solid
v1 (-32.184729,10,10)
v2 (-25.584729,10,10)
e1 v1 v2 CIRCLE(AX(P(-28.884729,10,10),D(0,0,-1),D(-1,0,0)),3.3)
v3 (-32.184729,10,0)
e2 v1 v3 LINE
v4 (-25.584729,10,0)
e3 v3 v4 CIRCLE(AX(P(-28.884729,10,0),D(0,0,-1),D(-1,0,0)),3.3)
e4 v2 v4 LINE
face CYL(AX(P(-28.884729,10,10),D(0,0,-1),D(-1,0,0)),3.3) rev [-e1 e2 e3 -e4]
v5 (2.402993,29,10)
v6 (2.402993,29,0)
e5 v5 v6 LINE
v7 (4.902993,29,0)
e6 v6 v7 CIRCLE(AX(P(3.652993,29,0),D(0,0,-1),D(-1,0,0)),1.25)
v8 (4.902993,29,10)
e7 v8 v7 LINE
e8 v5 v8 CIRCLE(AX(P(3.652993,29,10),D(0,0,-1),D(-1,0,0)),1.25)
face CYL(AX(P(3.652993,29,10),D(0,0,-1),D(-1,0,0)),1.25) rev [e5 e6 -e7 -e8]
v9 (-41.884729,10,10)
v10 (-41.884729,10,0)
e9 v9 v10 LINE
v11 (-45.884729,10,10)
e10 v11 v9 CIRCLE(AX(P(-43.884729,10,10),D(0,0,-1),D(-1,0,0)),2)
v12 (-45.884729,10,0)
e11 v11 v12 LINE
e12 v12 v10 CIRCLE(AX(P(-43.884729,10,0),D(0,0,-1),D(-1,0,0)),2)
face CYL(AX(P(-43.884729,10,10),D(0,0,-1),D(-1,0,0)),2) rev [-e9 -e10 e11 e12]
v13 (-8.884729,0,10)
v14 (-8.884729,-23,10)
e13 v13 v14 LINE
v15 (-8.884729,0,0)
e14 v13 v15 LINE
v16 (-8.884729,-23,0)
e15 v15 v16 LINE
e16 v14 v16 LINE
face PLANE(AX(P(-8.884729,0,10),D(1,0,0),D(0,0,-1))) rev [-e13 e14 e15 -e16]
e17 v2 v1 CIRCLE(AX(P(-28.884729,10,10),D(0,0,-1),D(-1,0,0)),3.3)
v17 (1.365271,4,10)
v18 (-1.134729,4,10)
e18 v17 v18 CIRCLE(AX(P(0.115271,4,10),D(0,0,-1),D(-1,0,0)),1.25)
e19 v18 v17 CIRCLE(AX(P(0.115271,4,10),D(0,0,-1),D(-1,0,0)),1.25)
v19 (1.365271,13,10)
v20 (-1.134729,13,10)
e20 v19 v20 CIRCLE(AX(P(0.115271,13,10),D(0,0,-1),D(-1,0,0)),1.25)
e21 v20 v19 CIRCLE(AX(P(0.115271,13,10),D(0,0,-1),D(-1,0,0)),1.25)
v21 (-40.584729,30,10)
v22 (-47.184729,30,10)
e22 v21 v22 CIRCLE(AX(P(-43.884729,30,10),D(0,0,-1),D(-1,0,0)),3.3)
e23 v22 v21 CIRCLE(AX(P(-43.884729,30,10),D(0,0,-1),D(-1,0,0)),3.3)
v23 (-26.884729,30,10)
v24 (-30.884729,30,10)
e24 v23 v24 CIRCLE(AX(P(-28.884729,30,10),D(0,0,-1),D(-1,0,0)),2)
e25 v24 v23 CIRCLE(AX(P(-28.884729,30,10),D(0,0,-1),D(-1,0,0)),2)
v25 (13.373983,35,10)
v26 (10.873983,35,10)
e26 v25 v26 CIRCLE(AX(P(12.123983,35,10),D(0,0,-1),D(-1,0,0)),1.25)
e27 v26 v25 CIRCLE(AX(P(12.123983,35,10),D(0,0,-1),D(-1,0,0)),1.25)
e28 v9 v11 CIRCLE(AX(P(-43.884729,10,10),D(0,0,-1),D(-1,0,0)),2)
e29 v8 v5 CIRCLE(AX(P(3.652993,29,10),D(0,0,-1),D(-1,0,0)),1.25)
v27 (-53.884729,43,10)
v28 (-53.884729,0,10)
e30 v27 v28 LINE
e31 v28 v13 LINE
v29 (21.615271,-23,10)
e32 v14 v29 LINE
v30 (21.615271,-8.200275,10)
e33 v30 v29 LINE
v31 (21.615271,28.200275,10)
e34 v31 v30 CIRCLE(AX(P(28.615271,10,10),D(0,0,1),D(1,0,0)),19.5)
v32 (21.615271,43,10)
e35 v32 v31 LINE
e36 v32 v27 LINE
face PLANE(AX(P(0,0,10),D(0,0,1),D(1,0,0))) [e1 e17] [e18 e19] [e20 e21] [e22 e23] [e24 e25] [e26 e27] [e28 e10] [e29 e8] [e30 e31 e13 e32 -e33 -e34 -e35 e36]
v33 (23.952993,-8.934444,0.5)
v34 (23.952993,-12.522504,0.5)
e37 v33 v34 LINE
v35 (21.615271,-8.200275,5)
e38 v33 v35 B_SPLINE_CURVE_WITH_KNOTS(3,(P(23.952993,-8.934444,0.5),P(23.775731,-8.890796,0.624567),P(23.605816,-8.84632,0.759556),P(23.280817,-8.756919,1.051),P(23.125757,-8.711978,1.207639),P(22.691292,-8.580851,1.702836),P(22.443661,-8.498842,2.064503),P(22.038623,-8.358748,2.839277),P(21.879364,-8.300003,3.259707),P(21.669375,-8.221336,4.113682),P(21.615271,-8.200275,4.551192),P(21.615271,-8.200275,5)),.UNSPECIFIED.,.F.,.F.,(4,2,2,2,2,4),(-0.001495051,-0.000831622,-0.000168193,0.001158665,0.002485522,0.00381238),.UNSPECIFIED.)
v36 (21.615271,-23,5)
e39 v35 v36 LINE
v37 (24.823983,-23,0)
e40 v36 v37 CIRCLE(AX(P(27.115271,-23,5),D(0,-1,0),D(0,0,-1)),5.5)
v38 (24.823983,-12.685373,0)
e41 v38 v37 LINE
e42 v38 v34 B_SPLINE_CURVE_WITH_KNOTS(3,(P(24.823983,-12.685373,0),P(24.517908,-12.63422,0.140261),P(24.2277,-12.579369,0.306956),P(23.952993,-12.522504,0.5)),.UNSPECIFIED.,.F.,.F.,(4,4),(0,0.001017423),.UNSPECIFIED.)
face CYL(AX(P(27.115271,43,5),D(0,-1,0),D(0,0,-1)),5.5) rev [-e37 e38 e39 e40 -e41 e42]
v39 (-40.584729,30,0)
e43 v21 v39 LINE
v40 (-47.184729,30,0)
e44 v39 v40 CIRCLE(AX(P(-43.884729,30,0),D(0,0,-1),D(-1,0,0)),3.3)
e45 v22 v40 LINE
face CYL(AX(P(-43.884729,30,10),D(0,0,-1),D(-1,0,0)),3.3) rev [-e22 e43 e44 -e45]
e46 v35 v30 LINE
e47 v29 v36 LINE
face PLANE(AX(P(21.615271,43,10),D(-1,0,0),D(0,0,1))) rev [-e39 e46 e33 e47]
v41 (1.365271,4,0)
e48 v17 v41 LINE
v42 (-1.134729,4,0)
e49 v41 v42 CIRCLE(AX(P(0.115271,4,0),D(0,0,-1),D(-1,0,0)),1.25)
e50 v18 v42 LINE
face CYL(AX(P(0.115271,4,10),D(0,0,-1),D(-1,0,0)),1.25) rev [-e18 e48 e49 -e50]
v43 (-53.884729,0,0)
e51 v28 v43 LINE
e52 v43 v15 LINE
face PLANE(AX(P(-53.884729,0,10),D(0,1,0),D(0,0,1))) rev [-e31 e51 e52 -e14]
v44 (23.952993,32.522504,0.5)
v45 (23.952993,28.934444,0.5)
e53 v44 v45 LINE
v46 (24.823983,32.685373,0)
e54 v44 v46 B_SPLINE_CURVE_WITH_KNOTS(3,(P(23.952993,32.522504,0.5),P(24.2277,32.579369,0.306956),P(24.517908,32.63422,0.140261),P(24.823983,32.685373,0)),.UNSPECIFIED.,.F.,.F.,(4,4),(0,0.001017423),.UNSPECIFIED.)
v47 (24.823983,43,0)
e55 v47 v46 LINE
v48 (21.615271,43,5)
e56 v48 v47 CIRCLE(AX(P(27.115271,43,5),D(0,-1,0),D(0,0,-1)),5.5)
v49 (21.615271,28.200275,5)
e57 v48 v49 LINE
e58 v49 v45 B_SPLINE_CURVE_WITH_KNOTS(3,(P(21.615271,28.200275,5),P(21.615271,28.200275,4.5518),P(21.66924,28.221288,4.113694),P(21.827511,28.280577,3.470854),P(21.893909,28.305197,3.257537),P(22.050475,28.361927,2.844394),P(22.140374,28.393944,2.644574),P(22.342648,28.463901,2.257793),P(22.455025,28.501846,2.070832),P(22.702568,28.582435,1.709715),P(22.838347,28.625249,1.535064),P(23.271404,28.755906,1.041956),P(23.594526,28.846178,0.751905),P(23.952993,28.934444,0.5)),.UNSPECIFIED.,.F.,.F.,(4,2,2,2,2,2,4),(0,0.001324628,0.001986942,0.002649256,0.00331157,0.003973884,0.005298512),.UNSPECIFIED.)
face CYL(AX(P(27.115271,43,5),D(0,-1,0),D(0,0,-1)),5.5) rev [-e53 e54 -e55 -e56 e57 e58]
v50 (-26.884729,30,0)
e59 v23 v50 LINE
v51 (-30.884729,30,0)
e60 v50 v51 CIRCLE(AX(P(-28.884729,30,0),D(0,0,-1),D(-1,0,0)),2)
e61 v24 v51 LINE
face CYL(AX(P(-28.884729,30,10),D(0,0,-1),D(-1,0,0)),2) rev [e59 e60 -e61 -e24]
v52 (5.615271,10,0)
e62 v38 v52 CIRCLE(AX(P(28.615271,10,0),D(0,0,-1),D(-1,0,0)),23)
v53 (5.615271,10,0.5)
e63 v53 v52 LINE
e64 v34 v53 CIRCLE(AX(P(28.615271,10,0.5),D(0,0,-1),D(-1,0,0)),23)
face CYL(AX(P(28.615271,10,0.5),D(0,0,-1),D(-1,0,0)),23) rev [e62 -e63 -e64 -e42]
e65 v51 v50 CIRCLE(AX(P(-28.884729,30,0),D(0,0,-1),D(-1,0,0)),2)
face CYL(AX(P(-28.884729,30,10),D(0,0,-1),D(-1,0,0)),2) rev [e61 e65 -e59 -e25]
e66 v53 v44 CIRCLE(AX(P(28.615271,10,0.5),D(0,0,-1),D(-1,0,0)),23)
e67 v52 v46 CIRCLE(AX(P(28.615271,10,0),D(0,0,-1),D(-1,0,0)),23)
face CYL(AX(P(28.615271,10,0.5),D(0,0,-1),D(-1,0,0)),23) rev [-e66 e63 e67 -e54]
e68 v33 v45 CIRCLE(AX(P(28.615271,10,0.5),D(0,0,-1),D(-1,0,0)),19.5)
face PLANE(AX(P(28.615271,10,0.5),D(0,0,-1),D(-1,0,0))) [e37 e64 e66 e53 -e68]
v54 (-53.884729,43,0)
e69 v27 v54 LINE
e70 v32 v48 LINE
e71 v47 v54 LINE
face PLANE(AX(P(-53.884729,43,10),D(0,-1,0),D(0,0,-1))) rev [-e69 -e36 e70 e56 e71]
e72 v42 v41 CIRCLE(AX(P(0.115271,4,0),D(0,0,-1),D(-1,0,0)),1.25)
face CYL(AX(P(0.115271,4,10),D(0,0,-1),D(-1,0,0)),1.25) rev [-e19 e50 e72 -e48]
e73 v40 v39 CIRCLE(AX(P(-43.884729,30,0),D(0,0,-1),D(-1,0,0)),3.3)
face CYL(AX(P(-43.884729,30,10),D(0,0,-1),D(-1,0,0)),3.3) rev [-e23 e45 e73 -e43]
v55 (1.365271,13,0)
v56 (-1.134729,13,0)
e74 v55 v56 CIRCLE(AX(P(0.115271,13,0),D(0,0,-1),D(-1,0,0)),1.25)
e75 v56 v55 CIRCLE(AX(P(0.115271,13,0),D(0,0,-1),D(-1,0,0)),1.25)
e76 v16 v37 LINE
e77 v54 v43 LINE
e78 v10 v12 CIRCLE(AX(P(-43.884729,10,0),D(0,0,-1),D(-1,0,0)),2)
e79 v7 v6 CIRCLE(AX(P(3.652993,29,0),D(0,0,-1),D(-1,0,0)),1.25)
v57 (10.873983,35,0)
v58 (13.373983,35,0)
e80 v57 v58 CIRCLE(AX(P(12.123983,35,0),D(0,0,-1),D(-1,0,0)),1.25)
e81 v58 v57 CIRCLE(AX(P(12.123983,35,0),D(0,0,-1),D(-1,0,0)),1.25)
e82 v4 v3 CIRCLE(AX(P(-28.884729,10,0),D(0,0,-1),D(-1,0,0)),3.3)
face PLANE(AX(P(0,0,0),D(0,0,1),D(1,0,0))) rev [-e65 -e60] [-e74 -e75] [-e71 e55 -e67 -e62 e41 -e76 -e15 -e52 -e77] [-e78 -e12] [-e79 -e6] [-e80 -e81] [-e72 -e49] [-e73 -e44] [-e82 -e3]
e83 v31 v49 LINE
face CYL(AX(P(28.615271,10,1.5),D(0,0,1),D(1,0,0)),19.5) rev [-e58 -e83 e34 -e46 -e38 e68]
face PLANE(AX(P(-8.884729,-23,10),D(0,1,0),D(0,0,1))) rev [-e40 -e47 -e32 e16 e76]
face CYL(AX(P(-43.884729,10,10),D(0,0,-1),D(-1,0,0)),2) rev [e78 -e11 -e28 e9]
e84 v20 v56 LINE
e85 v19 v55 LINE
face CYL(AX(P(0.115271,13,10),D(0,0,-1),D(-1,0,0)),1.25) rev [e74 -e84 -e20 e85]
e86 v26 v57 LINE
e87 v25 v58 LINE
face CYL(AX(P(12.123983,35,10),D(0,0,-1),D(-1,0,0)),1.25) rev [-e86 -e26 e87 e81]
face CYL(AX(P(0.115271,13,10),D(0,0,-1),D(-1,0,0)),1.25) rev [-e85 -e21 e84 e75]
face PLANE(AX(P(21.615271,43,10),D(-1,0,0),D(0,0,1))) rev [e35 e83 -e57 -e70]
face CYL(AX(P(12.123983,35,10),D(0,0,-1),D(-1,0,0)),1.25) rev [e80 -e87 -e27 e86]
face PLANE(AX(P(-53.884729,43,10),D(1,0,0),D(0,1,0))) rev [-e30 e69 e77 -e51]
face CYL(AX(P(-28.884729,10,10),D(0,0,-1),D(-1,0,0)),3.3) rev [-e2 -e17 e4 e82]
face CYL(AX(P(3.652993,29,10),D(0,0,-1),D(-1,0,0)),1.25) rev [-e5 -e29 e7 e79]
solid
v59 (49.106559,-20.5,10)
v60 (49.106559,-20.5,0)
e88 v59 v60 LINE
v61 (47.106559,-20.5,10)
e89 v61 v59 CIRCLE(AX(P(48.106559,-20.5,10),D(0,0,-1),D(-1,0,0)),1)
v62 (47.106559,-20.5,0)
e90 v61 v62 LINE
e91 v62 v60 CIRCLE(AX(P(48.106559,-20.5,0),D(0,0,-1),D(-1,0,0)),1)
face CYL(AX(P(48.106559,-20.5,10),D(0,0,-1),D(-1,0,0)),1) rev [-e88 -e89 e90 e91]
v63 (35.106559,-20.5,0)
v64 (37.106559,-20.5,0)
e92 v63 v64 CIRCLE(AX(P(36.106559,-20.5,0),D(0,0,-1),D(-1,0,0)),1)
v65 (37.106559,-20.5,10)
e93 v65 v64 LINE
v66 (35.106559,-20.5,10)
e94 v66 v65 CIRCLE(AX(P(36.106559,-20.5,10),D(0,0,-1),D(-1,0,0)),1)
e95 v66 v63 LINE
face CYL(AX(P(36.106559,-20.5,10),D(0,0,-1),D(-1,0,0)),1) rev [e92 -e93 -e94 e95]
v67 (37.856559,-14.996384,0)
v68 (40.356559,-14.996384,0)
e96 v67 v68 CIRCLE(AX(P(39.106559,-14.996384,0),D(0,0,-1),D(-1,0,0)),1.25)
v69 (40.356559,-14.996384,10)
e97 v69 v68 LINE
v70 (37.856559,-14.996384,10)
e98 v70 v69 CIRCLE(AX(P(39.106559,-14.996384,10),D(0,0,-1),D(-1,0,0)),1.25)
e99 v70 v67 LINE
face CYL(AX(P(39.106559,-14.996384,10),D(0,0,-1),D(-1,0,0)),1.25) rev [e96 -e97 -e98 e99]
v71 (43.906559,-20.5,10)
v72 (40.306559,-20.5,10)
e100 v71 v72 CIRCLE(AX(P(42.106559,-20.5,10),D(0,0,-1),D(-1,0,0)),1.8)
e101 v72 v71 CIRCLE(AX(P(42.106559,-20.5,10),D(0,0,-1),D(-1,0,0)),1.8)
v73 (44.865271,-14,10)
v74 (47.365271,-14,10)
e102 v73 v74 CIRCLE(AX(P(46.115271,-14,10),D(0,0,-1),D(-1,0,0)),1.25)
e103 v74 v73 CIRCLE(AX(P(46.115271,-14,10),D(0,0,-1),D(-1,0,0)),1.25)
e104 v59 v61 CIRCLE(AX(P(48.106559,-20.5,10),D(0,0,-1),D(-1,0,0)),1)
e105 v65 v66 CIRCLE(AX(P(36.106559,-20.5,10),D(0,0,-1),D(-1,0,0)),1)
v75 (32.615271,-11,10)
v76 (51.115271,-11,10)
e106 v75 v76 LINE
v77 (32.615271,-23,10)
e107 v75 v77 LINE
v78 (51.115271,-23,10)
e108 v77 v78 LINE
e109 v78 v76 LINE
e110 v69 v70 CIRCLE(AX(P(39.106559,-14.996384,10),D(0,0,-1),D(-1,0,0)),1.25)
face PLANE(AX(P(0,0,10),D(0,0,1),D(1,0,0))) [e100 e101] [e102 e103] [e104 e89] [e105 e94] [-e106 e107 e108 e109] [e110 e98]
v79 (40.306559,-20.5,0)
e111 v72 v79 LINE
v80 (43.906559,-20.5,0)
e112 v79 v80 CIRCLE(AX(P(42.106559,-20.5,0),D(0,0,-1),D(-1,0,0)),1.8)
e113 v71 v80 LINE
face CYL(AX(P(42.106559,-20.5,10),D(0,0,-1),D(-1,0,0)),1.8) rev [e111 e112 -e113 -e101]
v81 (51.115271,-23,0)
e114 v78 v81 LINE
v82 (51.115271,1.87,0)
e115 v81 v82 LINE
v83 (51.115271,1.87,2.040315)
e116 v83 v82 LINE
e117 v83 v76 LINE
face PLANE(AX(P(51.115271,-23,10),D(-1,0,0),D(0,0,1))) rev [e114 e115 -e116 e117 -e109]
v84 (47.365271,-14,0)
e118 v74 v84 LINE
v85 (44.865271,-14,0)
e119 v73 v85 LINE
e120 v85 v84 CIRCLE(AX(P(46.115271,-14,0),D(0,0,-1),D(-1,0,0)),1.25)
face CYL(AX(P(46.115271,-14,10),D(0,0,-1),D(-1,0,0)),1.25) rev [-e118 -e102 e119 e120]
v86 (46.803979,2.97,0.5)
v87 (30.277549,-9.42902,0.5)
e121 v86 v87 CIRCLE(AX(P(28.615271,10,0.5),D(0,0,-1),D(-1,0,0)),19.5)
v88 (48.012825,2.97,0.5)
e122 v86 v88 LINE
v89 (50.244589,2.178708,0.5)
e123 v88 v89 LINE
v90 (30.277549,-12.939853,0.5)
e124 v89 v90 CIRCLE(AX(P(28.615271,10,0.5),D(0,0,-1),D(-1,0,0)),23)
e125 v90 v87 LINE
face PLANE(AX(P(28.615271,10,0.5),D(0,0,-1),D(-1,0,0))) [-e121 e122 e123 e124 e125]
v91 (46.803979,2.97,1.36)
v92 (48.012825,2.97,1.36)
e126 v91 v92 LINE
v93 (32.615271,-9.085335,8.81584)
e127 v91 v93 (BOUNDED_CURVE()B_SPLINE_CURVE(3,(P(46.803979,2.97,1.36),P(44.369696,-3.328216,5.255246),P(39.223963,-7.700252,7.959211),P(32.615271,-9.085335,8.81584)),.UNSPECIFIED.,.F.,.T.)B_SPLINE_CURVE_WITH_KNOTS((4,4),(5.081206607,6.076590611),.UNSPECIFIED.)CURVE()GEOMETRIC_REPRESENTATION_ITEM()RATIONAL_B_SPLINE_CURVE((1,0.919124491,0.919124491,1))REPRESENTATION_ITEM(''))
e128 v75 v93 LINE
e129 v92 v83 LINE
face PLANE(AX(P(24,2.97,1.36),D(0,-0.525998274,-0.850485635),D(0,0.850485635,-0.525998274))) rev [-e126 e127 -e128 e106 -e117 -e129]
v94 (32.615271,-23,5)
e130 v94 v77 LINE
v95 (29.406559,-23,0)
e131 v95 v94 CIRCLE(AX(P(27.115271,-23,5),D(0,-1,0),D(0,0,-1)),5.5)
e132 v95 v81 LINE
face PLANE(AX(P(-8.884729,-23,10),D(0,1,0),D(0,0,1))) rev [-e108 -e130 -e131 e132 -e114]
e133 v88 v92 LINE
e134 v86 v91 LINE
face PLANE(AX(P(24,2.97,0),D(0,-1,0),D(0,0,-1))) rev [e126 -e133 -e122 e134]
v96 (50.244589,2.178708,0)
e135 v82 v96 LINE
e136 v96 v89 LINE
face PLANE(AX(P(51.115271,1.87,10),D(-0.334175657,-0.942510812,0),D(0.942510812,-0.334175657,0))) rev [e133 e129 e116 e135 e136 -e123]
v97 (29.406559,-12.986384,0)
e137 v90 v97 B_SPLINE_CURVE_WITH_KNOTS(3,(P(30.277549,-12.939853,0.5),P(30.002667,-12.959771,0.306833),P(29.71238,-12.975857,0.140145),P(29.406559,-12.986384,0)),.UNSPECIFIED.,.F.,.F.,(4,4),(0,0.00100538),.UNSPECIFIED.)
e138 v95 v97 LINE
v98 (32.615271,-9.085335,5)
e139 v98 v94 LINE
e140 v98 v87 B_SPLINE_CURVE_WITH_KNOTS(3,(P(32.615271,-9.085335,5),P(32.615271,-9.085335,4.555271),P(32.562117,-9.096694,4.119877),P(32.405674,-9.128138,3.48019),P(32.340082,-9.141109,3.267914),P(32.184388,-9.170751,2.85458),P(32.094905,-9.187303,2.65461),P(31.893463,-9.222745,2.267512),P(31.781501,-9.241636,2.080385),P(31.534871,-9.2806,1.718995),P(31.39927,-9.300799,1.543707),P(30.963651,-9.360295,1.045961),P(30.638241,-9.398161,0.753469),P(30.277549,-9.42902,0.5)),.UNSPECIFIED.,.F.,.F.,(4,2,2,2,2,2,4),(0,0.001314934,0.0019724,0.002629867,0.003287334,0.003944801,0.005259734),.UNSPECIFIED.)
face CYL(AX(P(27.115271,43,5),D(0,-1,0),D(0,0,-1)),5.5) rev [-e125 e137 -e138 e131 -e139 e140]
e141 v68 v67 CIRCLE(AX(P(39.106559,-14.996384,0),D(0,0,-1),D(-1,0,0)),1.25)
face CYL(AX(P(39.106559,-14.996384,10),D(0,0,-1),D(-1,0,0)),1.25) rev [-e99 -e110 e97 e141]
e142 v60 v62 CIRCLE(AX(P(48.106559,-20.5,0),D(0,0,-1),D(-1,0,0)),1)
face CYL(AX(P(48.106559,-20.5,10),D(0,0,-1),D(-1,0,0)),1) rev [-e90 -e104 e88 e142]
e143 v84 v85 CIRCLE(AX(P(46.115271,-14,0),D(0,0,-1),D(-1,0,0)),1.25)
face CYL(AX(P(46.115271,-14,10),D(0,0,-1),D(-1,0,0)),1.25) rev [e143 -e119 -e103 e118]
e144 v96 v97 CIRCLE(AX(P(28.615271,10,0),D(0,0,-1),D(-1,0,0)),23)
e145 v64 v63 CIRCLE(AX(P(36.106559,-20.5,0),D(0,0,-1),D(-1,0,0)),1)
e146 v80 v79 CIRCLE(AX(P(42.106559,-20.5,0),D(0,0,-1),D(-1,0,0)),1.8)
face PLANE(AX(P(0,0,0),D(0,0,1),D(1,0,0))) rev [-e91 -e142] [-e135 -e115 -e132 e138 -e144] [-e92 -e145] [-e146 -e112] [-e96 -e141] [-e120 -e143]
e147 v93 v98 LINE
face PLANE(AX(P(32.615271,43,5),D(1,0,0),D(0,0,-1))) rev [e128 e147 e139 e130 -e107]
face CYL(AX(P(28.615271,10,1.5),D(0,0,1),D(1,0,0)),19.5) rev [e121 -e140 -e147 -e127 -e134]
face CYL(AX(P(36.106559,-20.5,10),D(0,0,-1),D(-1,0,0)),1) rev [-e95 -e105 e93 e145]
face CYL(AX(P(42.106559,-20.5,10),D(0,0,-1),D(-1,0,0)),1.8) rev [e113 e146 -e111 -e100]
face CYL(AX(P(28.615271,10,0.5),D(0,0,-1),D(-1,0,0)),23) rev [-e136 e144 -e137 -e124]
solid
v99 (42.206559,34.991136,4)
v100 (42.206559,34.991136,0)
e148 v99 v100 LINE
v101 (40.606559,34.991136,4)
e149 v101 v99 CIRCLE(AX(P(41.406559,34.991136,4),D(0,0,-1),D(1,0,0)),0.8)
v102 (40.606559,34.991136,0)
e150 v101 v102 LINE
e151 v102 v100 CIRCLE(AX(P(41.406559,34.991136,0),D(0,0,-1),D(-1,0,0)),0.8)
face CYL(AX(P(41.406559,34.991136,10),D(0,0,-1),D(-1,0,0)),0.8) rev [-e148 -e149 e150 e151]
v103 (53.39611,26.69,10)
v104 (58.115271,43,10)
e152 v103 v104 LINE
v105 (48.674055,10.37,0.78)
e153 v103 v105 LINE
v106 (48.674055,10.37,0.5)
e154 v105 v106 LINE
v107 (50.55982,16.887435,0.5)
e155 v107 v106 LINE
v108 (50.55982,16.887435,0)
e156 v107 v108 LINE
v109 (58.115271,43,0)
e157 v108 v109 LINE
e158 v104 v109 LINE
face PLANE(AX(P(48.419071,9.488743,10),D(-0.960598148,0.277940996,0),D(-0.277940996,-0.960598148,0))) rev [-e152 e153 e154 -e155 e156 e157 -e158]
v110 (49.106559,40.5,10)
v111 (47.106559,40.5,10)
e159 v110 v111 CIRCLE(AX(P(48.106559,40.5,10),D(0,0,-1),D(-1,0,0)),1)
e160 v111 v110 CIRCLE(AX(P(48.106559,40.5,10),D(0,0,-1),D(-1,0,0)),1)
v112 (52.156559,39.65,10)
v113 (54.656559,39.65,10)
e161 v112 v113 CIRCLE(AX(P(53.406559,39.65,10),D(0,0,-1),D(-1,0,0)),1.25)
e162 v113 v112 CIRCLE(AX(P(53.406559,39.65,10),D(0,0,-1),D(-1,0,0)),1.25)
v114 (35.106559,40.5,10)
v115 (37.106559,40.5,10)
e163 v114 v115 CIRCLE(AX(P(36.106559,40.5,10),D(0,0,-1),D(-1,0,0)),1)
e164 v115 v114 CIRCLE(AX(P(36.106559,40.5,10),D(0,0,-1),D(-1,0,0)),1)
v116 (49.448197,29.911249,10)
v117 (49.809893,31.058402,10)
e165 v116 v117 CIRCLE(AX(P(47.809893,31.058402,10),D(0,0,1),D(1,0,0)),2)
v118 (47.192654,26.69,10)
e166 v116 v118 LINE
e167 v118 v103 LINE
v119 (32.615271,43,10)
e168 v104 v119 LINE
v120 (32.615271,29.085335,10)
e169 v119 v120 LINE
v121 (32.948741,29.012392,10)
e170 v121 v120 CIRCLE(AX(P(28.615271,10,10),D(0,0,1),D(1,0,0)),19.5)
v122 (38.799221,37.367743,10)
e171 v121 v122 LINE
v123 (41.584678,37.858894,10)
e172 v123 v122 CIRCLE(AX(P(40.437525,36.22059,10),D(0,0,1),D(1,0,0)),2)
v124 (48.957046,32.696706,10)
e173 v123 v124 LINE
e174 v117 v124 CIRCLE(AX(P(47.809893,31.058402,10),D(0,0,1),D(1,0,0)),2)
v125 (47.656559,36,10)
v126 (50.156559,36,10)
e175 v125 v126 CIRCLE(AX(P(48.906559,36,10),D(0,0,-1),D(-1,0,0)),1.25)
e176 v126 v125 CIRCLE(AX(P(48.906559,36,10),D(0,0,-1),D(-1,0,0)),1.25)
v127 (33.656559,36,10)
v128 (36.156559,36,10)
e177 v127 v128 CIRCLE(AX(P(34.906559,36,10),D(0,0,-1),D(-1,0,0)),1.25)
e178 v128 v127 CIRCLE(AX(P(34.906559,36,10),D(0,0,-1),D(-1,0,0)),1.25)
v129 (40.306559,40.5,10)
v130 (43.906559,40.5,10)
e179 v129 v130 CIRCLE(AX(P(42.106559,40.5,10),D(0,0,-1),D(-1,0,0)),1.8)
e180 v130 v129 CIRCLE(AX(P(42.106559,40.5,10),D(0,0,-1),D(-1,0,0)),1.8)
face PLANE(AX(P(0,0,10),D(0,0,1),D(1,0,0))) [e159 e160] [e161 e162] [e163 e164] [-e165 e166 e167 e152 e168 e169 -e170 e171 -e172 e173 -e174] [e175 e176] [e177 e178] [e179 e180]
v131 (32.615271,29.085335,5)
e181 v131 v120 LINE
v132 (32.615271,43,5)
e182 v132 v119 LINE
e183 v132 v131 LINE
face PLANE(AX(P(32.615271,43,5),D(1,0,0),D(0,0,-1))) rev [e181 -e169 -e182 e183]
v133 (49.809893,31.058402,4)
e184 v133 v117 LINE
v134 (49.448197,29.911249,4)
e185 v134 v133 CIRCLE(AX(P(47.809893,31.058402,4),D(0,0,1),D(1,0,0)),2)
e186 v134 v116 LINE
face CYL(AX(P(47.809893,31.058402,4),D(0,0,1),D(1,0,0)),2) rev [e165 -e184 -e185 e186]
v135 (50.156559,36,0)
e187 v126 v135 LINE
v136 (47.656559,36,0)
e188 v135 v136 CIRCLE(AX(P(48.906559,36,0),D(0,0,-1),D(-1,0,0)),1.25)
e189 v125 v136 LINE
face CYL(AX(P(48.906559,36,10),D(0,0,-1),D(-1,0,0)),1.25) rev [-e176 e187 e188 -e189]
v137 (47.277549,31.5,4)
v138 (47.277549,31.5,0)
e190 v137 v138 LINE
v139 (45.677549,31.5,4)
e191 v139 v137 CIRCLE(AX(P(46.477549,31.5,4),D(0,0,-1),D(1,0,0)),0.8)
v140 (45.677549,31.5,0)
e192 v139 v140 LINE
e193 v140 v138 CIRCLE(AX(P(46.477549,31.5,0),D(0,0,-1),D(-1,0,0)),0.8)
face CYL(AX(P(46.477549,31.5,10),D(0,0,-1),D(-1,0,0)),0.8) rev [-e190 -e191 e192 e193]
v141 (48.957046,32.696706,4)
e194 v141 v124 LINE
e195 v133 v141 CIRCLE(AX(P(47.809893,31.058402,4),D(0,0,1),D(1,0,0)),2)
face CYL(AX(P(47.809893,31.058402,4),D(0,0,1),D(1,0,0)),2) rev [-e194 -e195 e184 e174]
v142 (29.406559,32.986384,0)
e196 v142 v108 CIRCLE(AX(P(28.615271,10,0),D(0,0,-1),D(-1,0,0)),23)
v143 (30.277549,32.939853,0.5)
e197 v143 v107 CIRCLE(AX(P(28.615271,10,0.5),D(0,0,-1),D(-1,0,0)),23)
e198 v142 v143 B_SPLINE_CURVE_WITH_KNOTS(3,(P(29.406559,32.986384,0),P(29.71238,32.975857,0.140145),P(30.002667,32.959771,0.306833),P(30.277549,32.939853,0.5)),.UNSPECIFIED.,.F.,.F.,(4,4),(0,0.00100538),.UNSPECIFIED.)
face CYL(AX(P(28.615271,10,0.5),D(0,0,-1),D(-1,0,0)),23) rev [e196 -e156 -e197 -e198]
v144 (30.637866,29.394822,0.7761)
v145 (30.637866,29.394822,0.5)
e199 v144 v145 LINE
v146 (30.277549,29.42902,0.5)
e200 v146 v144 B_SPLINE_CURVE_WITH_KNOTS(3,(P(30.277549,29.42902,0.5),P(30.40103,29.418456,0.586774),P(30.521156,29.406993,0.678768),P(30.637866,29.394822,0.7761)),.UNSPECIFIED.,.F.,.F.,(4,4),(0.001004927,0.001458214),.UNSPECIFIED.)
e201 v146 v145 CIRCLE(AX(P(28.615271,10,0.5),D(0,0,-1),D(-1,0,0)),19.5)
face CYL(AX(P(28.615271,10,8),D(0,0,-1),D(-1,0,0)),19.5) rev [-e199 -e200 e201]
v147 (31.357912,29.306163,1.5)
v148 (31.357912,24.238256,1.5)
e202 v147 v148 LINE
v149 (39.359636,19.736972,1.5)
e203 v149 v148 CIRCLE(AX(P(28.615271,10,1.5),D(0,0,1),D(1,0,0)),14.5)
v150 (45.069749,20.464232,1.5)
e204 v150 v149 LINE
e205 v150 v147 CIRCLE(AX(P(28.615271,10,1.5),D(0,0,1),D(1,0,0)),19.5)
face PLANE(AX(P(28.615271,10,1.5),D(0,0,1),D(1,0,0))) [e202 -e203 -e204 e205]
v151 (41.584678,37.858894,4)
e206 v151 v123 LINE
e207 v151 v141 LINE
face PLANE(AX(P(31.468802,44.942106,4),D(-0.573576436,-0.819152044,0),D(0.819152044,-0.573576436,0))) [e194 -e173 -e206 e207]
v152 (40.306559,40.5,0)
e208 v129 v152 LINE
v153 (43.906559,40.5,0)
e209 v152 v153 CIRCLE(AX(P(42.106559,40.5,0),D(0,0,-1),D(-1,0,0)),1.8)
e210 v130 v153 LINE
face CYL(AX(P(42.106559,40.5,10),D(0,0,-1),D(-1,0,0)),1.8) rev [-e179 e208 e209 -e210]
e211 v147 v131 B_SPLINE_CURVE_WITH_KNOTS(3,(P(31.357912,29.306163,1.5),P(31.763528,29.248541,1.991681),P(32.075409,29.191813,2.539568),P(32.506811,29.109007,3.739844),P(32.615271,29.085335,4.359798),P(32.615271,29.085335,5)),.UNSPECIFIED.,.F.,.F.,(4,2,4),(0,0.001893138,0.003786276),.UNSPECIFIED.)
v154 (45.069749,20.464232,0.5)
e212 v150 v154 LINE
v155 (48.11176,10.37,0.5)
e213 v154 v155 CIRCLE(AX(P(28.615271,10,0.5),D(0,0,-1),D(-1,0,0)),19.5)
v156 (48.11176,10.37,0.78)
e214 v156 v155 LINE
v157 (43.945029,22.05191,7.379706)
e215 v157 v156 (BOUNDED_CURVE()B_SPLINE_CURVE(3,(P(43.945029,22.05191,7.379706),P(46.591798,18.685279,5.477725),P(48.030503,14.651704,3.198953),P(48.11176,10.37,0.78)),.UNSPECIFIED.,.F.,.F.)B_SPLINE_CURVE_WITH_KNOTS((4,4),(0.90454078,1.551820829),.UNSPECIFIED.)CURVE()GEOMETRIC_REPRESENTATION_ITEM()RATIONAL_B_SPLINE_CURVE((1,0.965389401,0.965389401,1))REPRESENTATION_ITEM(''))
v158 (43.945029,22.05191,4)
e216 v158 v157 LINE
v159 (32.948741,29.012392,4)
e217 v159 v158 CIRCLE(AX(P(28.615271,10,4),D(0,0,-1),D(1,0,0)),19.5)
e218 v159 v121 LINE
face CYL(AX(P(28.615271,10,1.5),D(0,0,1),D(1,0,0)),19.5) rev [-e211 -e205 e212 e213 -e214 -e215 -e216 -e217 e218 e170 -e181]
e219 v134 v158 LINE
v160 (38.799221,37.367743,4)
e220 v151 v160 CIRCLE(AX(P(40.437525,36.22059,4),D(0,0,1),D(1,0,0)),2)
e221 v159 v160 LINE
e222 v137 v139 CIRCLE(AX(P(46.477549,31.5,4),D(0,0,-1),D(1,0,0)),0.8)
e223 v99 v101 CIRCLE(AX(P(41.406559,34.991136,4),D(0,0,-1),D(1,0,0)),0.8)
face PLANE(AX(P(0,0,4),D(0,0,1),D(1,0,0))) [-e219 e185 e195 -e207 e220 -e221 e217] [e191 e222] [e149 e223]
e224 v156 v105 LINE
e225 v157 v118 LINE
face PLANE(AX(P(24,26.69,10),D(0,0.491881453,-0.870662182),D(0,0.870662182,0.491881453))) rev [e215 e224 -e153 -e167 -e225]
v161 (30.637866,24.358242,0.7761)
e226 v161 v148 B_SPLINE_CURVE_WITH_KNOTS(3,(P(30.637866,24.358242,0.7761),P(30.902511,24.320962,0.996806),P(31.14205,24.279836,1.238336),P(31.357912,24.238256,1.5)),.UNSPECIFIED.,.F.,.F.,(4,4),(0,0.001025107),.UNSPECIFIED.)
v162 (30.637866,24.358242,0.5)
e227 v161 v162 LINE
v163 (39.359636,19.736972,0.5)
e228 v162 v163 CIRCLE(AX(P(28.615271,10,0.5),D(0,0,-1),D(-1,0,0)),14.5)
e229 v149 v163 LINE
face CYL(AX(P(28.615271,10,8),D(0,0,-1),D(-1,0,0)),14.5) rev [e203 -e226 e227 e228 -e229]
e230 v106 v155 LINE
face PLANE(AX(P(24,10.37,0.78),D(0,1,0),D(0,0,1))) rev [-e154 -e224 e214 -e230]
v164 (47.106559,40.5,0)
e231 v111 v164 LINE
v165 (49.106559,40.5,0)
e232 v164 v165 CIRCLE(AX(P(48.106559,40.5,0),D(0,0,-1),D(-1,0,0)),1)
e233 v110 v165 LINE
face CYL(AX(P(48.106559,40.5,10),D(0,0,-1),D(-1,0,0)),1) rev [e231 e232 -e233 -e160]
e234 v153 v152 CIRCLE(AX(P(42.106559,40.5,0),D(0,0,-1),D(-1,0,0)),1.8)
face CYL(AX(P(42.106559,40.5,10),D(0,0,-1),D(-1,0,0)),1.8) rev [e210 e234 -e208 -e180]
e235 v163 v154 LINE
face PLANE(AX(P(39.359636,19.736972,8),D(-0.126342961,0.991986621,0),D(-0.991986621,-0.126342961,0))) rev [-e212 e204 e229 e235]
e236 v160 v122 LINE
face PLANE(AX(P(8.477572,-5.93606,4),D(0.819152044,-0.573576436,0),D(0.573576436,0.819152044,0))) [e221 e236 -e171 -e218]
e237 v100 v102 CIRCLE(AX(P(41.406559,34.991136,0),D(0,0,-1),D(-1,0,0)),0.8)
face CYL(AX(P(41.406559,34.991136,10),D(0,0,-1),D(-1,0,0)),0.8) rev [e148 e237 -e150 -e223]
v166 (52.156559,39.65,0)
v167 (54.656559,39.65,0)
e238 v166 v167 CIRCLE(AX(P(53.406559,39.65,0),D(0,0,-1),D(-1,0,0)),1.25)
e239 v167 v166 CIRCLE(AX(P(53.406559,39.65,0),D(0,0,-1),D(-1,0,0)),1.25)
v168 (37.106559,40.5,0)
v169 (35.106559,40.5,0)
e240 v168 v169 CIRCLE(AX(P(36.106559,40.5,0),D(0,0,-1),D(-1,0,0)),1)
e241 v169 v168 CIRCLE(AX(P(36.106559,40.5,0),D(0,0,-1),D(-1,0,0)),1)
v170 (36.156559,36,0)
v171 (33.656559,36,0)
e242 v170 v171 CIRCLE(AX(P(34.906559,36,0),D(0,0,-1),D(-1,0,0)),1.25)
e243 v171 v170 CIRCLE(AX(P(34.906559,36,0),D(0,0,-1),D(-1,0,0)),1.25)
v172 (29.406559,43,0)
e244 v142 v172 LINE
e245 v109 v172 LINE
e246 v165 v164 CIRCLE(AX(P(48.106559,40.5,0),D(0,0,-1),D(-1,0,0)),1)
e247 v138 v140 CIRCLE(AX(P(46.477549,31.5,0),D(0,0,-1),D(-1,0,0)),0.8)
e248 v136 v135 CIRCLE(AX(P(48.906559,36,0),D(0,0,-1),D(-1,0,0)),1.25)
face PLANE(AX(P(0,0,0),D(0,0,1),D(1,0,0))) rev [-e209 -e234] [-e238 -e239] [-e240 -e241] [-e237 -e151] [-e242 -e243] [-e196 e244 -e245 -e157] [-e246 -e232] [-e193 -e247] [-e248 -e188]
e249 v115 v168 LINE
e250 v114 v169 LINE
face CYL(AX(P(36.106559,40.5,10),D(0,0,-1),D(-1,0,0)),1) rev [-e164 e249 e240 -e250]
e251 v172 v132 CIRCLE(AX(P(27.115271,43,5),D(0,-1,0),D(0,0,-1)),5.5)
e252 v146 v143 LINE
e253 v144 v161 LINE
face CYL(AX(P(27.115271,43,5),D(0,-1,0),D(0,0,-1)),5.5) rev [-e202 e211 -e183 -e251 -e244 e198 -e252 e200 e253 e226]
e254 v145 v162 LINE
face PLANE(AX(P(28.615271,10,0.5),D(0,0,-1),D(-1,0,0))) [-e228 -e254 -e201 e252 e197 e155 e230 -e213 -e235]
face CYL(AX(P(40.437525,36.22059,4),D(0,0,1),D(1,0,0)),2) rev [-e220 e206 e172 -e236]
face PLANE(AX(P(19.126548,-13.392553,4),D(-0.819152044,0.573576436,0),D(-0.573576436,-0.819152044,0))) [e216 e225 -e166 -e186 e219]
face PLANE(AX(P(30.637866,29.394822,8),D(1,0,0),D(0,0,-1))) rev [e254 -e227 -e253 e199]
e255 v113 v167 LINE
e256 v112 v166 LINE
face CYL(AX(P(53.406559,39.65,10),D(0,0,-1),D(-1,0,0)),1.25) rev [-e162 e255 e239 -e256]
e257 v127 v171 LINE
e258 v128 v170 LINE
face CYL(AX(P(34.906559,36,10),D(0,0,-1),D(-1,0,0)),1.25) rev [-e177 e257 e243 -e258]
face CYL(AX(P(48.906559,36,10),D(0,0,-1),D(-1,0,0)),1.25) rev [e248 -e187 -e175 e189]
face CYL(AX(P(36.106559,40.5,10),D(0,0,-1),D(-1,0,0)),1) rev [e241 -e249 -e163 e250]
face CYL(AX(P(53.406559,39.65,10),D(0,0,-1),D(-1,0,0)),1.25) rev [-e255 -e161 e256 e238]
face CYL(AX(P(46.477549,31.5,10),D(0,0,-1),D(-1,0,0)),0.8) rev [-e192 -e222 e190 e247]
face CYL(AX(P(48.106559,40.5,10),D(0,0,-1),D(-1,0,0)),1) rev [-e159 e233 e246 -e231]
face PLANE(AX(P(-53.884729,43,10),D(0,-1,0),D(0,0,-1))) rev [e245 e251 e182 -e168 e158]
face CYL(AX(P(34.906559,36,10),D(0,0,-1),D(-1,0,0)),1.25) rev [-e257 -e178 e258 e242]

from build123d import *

# Parameters (mm, degrees)
EXTRUDE_1_DEPTH     = 10
CUT_EXTRUDE_2_DEPTH = 89.50641067
CUT_EXTRUDE_3_DEPTH = 73.982084992
CUT_EXTRUDE_4_DEPTH = 56
SKETCH_7_R          = 23
CUT_EXTRUDE_5_DEPTH = 0.5
SKETCH_8_R          = 19.5
CUT_EXTRUDE_6_DEPTH = 8.5
CUT_EXTRUDE_7_DEPTH = 8
SKETCH_10_R         = 2
SKETCH_10_R_2       = 3.3
SKETCH_10_R_3       = 1.25
SKETCH_10_R_4       = 1
SKETCH_10_R_5       = 1.8
SKETCH_10_R_6       = 0.8
CUT_EXTRUDE_8_DEPTH = 73.982085064
CUT_EXTRUDE_9_DEPTH = 6


with BuildPart() as part:
    # 草图1 → 凸台-拉伸1 (new body)
    with BuildSketch(Plane.XY):
        Polygon((-53.884728945, 0), (-8.884728945, 0), (-8.884728945, -23), (58.115271055, -23), (58.115271055, 43), (-53.884728945, 43), align=None)
    extrude(amount=EXTRUDE_1_DEPTH)

    # 草图3 → 切除-拉伸2 (cut, through all)
    with BuildSketch(Plane.XZ.offset(23)):
        with BuildLine():
            Line((32.615271055, 5), (32.615271055, 10))
            Line((32.615271055, 10), (21.615271055, 10))
            Line((21.615271055, 10), (21.615271055, 5))
            ThreePointArc((21.615271055, 5), (27.115271055, -0.5), (32.615271055, 5))
        make_face()
    extrude(amount=-CUT_EXTRUDE_2_DEPTH, mode=Mode.SUBTRACT)


with BuildPart() as cut_extrude_2_piece_1:
    # of the separate pieces the step leaves, piece 1, a body of its own (cut_extrude_2_pieces)
    add(part.part.solids().sort_by_distance((-53.884728945, 0, 0))[0])


with BuildPart() as cut_extrude_2_piece_2:
    # of the separate pieces the step leaves, piece 2, a body of its own (cut_extrude_2_pieces)
    add(part.part.solids().sort_by_distance((58.115271055, 43, 0))[0])

    # 草图4 → 切除-拉伸3 (cut, through all)
    with BuildSketch(Plane(origin=(0, 0, 0), x_dir=(-1, 0, 0), z_dir=(0, 0, -1))):
        Polygon((-58.115271055, -23), (-58.115271055, 43), (-48.419070628, 9.488742909), (-45.499700026, 10), (-44.487463913, 4.219948433), (-51.115271055, 1.87), (-51.115271055, -23), align=None)
    extrude(amount=-CUT_EXTRUDE_3_DEPTH, mode=Mode.SUBTRACT)

    # 草图6 → 切除-拉伸4 (cut)
    with BuildSketch(Plane(origin=(80, 0, 0), x_dir=(0, 0, -1), z_dir=(1, 0, 0))):
        Polygon((-10, 26.69), (-0.78, 10.37), (0, 10.37), (0, 2.97), (-1.36, 2.97), (-10, -11), align=None)
    extrude(amount=-CUT_EXTRUDE_4_DEPTH, mode=Mode.SUBTRACT)


with BuildPart() as cut_extrude_4_piece_1:
    # of the separate pieces the step leaves, piece 1, a body of its own (cut_extrude_4_pieces)
    add(cut_extrude_2_piece_2.part.solids().sort_by_distance((58.115271055, 43, 0))[0])


with BuildPart() as cut_extrude_4_piece_2:
    # of the separate pieces the step leaves, piece 2, a body of its own (cut_extrude_4_pieces)
    add(cut_extrude_2_piece_2.part.solids().sort_by_distance((48.012825165, 2.97, 0))[0])


with BuildPart() as cut_extrude_5_tool:
    # 草图7 → 切除-拉伸5 (new body)
    with BuildSketch(Plane(origin=(0, 0, 0), x_dir=(-1, 0, 0), z_dir=(0, 0, -1))):
        with Locations((-28.615271055, 10)):
            Circle(SKETCH_7_R)
    extrude(amount=-CUT_EXTRUDE_5_DEPTH)


with BuildPart() as cut_extrude_2_piece_1_1:
    add(cut_extrude_2_piece_1.part)

    # 切除-拉伸5: cut by cut_extrude_5_tool
    add(cut_extrude_5_tool.part, mode=Mode.SUBTRACT)


with BuildPart() as cut_extrude_4_piece_1_1:
    add(cut_extrude_4_piece_1.part)

    # 切除-拉伸5: cut by cut_extrude_5_tool
    add(cut_extrude_5_tool.part, mode=Mode.SUBTRACT)


with BuildPart() as cut_extrude_4_piece_2_1:
    add(cut_extrude_4_piece_2.part)

    # 切除-拉伸5: cut by cut_extrude_5_tool
    add(cut_extrude_5_tool.part, mode=Mode.SUBTRACT)


with BuildPart() as cut_extrude_6_tool:
    # 草图8 → 切除-拉伸6 (new body)
    with BuildSketch(Plane.XY.offset(10)):
        with Locations((28.615271055, 10)):
            Circle(SKETCH_8_R)
    extrude(amount=-CUT_EXTRUDE_6_DEPTH)


with BuildPart() as cut_extrude_2_piece_1_2:
    add(cut_extrude_2_piece_1_1.part)

    # 切除-拉伸6: cut by cut_extrude_6_tool
    add(cut_extrude_6_tool.part, mode=Mode.SUBTRACT)


with BuildPart() as cut_extrude_4_piece_1_2:
    add(cut_extrude_4_piece_1_1.part)

    # 切除-拉伸6: cut by cut_extrude_6_tool
    add(cut_extrude_6_tool.part, mode=Mode.SUBTRACT)


with BuildPart() as cut_extrude_4_piece_2_2:
    add(cut_extrude_4_piece_2_1.part)

    # 切除-拉伸6: cut by cut_extrude_6_tool
    add(cut_extrude_6_tool.part, mode=Mode.SUBTRACT)


with BuildPart() as cut_extrude_7_tool:
    # 草图9 → 切除-拉伸7 (new body)
    with BuildSketch(Plane(origin=(0, 0, 0), x_dir=(-1, 0, 0), z_dir=(0, 0, -1))):
        with BuildLine():
            Line((-39.359635932, 19.736971983), (-45.069748889, 20.464232375))
            ThreePointArc((-45.069748889, 20.464232375), (-18.354208401, -6.58193575), (-30.637865502, 29.394821775))
            Line((-30.637865502, 29.394821775), (-30.637865502, 24.358241943))
            ThreePointArc((-30.637865502, 24.358241943), (-35.404074087, 22.812577937), (-39.359635932, 19.736971983))
        make_face()
    extrude(amount=-CUT_EXTRUDE_7_DEPTH)


with BuildPart() as cut_extrude_2_piece_1_3:
    add(cut_extrude_2_piece_1_2.part)

    # 切除-拉伸7: cut by cut_extrude_7_tool
    add(cut_extrude_7_tool.part, mode=Mode.SUBTRACT)


with BuildPart() as cut_extrude_4_piece_1_3:
    add(cut_extrude_4_piece_1_2.part)

    # 切除-拉伸7: cut by cut_extrude_7_tool
    add(cut_extrude_7_tool.part, mode=Mode.SUBTRACT)


with BuildPart() as cut_extrude_4_piece_2_3:
    add(cut_extrude_4_piece_2_2.part)

    # 切除-拉伸7: cut by cut_extrude_7_tool
    add(cut_extrude_7_tool.part, mode=Mode.SUBTRACT)


with BuildPart() as cut_extrude_8_tool:
    # 草图10 → 切除-拉伸8 (new, through all)
    with BuildSketch(Plane(origin=(0, 0, 0), x_dir=(-1, 0, 0), z_dir=(0, 0, -1))):
        with Locations((43.884728945, 10)):
            Circle(SKETCH_10_R)
        with Locations((28.884728945, 10)):
            Circle(SKETCH_10_R_2)
        with Locations((28.884728945, 30)):
            Circle(SKETCH_10_R)
        with Locations((43.884728945, 30)):
            Circle(SKETCH_10_R_2)
        with Locations((-0.115271055, 4)):
            Circle(SKETCH_10_R_3)
        with Locations((-0.115271055, 13)):
            Circle(SKETCH_10_R_3)
        with Locations((-3.652993394, 29)):
            Circle(SKETCH_10_R_3)
        with Locations((-12.123983207, 35)):
            Circle(SKETCH_10_R_3)
        with Locations((-48.106558902, -20.5)):
            Circle(SKETCH_10_R_4)
        with Locations((-42.106558902, -20.5)):
            Circle(SKETCH_10_R_5)
        with Locations((-36.106558902, -20.5)):
            Circle(SKETCH_10_R_4)
        with Locations((-46.115271055, -14)):
            Circle(SKETCH_10_R_3)
        with Locations((-39.106558902, -14.996384308)):
            Circle(SKETCH_10_R_3)
        with Locations((-34.906558902, 36)):
            Circle(SKETCH_10_R_3)
        with Locations((-36.106558902, 40.5)):
            Circle(SKETCH_10_R_4)
        with Locations((-41.406558902, 34.99113626)):
            Circle(SKETCH_10_R_6)
        with Locations((-42.106558902, 40.5)):
            Circle(SKETCH_10_R_5)
        with Locations((-48.906558902, 36)):
            Circle(SKETCH_10_R_3)
        with Locations((-46.477548715, 31.5)):
            Circle(SKETCH_10_R_6)
        with Locations((-48.106558902, 40.5)):
            Circle(SKETCH_10_R_4)
        with Locations((-53.406558902, 39.65)):
            Circle(SKETCH_10_R_3)
    extrude(amount=-CUT_EXTRUDE_8_DEPTH)


with BuildPart() as cut_extrude_2_piece_1_4:
    add(cut_extrude_2_piece_1_3.part)

    # 切除-拉伸8: cut by cut_extrude_8_tool
    add(cut_extrude_8_tool.part, mode=Mode.SUBTRACT)


with BuildPart() as cut_extrude_4_piece_1_4:
    add(cut_extrude_4_piece_1_3.part)

    # 切除-拉伸8: cut by cut_extrude_8_tool
    add(cut_extrude_8_tool.part, mode=Mode.SUBTRACT)

    # 草图11 → 切除-拉伸9 (cut)
    with BuildSketch(Plane.XY.offset(10)):
        with BuildLine():
            Line((32.948740967, 29.01239171), (38.799220617, 37.367742561))
            ThreePointArc((38.799220617, 37.367742561), (40.090228351, 38.190205195), (41.584677579, 37.858893777))
            Line((41.584677579, 37.858893777), (48.957045977, 32.69670585))
            ThreePointArc((48.957045977, 32.69670585), (49.77950861, 31.405698117), (49.448197193, 29.911248889))
            Line((49.448197193, 29.911248889), (43.94502872, 22.051909804))
            ThreePointArc((43.94502872, 22.051909804), (39.044686512, 26.476568005), (32.948740967, 29.01239171))
        make_face()
    extrude(amount=-CUT_EXTRUDE_9_DEPTH, mode=Mode.SUBTRACT)


with BuildPart() as cut_extrude_4_piece_2_4:
    add(cut_extrude_4_piece_2_3.part)

    # 切除-拉伸8: cut by cut_extrude_8_tool
    add(cut_extrude_8_tool.part, mode=Mode.SUBTRACT)


solid = Compound([cut_extrude_2_piece_1_4.part, cut_extrude_4_piece_1_4.part, cut_extrude_4_piece_2_4.part])
